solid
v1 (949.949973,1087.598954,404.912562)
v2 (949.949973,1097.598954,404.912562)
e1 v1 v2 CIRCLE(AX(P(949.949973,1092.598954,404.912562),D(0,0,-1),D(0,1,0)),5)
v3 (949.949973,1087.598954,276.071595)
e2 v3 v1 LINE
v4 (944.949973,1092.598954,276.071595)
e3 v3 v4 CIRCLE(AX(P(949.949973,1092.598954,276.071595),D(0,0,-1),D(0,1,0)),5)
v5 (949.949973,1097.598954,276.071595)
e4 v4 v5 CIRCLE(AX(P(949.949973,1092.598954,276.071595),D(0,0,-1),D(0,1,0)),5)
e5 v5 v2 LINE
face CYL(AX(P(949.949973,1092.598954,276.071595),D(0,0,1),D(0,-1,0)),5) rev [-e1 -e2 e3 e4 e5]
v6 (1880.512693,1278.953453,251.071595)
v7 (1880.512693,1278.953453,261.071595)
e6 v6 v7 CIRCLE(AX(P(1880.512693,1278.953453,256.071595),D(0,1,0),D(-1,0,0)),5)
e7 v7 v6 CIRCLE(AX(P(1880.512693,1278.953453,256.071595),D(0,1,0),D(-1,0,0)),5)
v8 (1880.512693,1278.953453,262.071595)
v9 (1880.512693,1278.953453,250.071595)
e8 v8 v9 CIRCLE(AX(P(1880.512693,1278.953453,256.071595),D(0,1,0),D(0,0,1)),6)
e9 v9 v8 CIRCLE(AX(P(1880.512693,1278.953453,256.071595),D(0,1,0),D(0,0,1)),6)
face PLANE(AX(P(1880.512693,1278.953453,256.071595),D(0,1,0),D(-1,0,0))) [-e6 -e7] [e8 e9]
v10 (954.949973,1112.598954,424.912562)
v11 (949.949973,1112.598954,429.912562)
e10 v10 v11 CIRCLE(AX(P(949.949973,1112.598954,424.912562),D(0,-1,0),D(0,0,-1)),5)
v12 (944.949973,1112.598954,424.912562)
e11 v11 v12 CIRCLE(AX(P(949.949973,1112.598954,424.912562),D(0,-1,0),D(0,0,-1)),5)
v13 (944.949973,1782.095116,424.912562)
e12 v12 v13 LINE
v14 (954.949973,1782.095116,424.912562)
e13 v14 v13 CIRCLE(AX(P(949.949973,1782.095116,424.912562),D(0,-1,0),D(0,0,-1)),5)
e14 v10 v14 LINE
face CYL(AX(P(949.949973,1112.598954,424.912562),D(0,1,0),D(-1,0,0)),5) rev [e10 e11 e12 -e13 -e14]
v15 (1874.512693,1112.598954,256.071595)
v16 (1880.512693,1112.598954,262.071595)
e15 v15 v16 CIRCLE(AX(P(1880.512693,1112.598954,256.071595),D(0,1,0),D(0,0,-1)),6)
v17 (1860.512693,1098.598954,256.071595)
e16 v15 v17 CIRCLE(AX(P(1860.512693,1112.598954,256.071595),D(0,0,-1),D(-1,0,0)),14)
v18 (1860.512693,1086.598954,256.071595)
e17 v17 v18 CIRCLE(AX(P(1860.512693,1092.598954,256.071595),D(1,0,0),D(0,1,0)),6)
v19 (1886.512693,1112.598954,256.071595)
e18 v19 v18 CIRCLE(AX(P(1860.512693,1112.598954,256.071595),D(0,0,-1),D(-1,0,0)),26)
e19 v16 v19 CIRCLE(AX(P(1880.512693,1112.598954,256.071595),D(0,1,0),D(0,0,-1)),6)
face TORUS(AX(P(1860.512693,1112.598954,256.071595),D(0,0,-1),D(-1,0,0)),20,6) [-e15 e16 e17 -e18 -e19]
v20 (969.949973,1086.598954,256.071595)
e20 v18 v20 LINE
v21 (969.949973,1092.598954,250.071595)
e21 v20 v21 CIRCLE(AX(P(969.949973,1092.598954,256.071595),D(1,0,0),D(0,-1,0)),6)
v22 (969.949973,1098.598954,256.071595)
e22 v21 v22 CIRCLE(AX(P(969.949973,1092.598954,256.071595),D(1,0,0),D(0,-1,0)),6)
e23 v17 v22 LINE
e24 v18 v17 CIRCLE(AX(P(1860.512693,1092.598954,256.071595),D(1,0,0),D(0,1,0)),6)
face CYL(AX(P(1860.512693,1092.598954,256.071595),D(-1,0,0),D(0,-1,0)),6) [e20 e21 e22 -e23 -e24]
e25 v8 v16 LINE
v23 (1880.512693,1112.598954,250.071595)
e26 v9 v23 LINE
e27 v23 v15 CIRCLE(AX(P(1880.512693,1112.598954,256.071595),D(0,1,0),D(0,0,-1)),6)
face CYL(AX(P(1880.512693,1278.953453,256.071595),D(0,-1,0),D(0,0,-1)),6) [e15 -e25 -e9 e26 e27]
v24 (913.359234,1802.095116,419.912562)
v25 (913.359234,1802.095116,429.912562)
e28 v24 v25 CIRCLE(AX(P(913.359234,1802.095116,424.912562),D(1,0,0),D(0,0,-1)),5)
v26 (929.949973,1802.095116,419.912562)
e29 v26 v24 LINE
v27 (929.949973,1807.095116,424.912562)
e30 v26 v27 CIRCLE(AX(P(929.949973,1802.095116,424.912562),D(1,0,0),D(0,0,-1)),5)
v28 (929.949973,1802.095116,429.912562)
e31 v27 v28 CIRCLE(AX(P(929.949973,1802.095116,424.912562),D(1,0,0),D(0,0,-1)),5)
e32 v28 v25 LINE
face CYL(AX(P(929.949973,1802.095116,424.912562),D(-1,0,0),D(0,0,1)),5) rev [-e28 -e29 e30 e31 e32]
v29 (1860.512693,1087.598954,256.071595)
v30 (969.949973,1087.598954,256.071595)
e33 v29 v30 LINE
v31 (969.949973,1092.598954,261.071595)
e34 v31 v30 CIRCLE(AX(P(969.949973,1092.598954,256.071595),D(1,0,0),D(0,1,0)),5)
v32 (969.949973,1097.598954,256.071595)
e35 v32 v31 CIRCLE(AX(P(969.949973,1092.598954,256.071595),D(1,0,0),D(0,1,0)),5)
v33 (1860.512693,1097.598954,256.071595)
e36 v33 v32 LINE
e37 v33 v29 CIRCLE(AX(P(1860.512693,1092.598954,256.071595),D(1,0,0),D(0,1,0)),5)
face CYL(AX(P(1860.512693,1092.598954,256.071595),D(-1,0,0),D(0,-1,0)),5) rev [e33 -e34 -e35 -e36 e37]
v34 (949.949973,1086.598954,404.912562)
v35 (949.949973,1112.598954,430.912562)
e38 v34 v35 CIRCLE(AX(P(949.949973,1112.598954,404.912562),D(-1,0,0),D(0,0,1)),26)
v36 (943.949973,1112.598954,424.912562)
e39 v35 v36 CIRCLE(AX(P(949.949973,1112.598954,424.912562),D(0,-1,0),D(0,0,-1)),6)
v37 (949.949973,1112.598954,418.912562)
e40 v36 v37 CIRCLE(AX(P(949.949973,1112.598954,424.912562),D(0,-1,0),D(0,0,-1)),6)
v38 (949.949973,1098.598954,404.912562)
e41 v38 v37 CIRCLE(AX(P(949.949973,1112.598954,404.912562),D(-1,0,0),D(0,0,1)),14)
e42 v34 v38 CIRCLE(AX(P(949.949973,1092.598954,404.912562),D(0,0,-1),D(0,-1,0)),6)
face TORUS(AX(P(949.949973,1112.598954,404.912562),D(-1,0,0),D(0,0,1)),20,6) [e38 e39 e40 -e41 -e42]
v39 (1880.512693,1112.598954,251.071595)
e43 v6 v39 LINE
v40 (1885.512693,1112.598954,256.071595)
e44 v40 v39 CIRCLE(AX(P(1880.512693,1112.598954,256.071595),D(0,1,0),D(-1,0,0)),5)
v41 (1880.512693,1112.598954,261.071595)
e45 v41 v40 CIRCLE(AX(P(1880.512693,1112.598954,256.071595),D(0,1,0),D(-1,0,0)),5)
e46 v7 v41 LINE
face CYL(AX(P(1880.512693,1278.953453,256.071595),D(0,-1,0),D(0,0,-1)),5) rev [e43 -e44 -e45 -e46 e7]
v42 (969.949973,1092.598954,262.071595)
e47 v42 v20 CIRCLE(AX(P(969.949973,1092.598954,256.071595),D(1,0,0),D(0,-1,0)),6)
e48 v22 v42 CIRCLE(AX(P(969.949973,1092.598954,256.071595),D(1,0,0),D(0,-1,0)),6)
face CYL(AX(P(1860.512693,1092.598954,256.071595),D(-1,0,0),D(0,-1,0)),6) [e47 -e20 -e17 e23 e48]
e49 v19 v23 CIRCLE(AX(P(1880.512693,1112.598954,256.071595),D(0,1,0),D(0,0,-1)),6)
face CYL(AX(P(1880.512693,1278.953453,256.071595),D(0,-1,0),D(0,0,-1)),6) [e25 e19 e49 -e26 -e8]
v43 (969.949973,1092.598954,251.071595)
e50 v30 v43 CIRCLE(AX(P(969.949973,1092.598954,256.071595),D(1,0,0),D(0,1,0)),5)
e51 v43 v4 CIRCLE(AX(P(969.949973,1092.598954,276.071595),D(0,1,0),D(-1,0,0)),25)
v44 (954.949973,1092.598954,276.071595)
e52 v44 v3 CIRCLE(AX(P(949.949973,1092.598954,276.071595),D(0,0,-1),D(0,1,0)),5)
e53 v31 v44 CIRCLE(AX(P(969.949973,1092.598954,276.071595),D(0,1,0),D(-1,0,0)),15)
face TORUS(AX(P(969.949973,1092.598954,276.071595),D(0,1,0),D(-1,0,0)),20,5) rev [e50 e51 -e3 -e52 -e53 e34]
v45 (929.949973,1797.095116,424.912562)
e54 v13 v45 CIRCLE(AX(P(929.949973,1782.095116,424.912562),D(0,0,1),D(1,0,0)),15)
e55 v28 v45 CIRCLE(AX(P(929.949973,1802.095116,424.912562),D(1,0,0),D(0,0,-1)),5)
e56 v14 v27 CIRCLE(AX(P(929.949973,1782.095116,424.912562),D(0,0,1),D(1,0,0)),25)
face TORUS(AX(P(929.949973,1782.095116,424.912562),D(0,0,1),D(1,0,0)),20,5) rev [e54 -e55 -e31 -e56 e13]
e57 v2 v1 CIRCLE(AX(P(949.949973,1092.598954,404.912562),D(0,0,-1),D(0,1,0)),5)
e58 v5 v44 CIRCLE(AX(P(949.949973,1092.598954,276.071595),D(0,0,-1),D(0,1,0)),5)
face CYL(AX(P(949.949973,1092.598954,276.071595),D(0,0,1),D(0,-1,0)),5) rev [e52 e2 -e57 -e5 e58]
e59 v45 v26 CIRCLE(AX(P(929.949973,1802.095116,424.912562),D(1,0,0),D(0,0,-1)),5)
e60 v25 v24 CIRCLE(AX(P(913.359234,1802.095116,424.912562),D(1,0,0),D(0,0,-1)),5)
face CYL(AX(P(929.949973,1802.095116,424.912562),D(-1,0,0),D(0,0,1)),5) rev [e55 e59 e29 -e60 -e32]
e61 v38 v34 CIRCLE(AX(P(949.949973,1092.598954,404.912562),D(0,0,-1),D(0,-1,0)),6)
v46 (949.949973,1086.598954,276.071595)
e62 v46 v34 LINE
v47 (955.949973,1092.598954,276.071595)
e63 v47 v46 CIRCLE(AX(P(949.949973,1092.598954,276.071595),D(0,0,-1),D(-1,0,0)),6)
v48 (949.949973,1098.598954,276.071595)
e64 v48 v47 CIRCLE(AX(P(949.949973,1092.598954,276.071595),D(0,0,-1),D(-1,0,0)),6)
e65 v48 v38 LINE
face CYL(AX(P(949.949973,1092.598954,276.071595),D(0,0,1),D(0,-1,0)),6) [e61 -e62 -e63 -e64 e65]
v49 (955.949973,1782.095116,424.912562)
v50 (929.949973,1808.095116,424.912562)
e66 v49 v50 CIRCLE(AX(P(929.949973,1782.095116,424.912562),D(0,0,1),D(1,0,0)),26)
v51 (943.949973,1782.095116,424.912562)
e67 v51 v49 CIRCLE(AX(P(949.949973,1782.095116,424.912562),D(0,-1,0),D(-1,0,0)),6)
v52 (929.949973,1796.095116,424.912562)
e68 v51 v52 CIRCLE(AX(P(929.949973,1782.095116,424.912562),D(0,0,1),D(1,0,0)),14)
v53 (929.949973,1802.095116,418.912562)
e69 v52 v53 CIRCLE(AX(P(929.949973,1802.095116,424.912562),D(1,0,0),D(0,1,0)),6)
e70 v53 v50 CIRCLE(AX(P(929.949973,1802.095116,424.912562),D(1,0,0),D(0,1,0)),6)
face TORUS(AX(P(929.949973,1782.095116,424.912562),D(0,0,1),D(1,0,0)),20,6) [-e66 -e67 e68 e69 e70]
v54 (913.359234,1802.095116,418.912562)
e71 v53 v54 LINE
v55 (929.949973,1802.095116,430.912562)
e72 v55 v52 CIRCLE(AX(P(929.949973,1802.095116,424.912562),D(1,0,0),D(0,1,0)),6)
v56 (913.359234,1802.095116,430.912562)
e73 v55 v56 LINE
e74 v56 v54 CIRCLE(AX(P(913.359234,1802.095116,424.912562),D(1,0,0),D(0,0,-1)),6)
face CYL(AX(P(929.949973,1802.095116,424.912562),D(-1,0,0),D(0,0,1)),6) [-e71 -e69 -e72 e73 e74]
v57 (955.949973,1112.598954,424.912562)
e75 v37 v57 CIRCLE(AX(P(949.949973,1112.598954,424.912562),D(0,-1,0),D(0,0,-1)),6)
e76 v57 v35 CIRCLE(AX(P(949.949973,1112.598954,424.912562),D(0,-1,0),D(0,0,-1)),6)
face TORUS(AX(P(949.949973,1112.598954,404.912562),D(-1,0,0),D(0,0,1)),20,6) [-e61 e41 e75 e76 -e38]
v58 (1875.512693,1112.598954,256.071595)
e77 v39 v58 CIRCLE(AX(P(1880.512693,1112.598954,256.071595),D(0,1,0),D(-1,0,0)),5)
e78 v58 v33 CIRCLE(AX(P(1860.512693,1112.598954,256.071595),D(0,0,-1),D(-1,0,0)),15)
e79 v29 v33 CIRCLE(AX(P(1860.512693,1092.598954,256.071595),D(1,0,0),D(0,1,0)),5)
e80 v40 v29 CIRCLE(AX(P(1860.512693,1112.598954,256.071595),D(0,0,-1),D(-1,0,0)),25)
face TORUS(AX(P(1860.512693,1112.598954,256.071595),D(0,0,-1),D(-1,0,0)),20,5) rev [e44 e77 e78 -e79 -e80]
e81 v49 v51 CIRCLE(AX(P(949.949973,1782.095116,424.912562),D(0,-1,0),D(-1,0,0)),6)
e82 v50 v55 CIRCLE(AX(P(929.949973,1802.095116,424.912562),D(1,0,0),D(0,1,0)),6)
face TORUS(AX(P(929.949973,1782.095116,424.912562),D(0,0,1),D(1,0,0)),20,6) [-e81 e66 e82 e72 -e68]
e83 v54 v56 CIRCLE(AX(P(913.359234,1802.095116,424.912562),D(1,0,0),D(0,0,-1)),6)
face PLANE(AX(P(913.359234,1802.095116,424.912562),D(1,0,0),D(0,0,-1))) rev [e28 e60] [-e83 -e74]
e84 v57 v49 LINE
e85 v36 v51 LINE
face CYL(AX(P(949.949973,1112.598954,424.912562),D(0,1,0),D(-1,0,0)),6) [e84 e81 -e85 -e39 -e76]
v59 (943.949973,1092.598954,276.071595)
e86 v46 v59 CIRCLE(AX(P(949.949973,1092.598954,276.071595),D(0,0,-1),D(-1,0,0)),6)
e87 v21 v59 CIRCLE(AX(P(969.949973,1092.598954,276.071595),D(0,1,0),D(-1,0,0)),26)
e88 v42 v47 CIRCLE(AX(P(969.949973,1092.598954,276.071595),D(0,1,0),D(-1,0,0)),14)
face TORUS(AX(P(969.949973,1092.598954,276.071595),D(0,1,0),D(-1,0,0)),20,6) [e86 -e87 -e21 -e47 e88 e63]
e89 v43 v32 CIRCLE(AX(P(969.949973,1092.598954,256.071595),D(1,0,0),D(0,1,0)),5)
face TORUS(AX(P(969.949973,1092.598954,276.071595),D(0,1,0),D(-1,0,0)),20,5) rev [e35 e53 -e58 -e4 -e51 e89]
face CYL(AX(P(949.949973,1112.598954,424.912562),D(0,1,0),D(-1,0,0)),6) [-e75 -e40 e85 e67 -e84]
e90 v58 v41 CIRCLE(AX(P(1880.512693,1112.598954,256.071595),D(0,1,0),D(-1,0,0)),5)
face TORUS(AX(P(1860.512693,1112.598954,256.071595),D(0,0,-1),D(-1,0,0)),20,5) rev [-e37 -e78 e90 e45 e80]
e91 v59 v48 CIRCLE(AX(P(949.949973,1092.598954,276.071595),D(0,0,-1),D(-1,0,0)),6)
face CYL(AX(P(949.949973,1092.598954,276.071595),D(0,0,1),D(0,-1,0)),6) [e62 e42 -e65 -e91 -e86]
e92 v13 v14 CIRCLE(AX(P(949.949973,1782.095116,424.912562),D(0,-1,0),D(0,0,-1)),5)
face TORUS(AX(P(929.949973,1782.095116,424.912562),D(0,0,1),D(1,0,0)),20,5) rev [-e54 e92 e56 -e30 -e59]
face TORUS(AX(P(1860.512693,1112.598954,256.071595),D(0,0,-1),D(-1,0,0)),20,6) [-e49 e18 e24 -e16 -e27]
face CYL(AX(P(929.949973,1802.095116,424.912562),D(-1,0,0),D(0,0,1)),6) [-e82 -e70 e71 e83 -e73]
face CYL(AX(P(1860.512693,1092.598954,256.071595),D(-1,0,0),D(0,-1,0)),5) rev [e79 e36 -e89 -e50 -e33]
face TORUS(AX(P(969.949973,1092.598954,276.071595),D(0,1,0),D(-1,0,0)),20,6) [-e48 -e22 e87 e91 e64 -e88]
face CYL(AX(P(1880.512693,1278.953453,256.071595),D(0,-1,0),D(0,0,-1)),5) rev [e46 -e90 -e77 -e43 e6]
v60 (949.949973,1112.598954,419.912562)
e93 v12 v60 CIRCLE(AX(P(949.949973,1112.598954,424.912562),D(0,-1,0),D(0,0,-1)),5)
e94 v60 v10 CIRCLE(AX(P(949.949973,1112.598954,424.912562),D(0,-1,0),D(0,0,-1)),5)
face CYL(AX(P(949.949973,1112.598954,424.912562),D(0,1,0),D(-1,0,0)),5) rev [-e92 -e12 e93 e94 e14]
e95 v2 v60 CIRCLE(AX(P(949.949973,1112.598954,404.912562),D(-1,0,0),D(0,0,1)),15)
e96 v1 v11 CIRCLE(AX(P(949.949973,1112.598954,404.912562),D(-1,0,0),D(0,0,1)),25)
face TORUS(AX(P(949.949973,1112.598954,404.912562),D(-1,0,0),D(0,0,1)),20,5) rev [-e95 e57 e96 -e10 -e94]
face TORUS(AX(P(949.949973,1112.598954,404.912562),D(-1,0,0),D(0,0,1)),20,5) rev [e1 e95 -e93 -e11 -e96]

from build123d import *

# Parameters (mm, degrees)
SWEEP_1_PROFILE_R   = 6
SWEEP_1_PROFILE_R_2 = 5


with BuildPart() as part:
    # 扫描-薄件1: sweep along a curve in space
    with BuildLine() as sweep_1_path:
        Line((1880.512693362, 1112.598953747, 256.07159483), (1880.512693362, 1278.953453372, 256.07159483))
        ThreePointArc((1860.512693362, 1092.598953747, 256.07159483), (1874.654828986, 1098.456818123, 256.07159483), (1880.512693362, 1112.598953747, 256.07159483))
        Line((1860.512693362, 1092.598953747, 256.07159483), (969.949972589, 1092.598953747, 256.07159483))
        ThreePointArc((949.949972589, 1092.598953747, 276.07159483), (955.807836965, 1092.598953747, 261.929459206), (969.949972589, 1092.598953747, 256.07159483))
        Line((949.949972589, 1092.598953747, 276.07159483), (949.949972589, 1092.598953747, 404.912562332))
        ThreePointArc((949.949972589, 1092.598953747, 404.912562332), (949.949972589, 1098.456818123, 419.054697956), (949.949972589, 1112.598953747, 424.912562332))
        Line((949.949972589, 1112.598953747, 424.912562332), (949.949972589, 1782.095116422, 424.912562332))
        ThreePointArc((949.949972589, 1782.095116422, 424.912562332), (944.092108213, 1796.237252046, 424.912562332), (929.949972589, 1802.095116422, 424.912562332))
        Line((929.949972589, 1802.095116422, 424.912562332), (913.359234408, 1802.095116422, 424.912562332))
    # 扫描-薄件1 profile (on start of the path) → 扫描-薄件1 (sweep)
    with BuildSketch(Plane(origin=(913.359234408, 1802.095116422, 424.912562332), x_dir=(0, 0, 1), z_dir=(1, 0, 0))):
        Circle(SWEEP_1_PROFILE_R)
        Circle(SWEEP_1_PROFILE_R_2, mode=Mode.SUBTRACT)
    sweep(path=sweep_1_path.line)


solid = part.part
